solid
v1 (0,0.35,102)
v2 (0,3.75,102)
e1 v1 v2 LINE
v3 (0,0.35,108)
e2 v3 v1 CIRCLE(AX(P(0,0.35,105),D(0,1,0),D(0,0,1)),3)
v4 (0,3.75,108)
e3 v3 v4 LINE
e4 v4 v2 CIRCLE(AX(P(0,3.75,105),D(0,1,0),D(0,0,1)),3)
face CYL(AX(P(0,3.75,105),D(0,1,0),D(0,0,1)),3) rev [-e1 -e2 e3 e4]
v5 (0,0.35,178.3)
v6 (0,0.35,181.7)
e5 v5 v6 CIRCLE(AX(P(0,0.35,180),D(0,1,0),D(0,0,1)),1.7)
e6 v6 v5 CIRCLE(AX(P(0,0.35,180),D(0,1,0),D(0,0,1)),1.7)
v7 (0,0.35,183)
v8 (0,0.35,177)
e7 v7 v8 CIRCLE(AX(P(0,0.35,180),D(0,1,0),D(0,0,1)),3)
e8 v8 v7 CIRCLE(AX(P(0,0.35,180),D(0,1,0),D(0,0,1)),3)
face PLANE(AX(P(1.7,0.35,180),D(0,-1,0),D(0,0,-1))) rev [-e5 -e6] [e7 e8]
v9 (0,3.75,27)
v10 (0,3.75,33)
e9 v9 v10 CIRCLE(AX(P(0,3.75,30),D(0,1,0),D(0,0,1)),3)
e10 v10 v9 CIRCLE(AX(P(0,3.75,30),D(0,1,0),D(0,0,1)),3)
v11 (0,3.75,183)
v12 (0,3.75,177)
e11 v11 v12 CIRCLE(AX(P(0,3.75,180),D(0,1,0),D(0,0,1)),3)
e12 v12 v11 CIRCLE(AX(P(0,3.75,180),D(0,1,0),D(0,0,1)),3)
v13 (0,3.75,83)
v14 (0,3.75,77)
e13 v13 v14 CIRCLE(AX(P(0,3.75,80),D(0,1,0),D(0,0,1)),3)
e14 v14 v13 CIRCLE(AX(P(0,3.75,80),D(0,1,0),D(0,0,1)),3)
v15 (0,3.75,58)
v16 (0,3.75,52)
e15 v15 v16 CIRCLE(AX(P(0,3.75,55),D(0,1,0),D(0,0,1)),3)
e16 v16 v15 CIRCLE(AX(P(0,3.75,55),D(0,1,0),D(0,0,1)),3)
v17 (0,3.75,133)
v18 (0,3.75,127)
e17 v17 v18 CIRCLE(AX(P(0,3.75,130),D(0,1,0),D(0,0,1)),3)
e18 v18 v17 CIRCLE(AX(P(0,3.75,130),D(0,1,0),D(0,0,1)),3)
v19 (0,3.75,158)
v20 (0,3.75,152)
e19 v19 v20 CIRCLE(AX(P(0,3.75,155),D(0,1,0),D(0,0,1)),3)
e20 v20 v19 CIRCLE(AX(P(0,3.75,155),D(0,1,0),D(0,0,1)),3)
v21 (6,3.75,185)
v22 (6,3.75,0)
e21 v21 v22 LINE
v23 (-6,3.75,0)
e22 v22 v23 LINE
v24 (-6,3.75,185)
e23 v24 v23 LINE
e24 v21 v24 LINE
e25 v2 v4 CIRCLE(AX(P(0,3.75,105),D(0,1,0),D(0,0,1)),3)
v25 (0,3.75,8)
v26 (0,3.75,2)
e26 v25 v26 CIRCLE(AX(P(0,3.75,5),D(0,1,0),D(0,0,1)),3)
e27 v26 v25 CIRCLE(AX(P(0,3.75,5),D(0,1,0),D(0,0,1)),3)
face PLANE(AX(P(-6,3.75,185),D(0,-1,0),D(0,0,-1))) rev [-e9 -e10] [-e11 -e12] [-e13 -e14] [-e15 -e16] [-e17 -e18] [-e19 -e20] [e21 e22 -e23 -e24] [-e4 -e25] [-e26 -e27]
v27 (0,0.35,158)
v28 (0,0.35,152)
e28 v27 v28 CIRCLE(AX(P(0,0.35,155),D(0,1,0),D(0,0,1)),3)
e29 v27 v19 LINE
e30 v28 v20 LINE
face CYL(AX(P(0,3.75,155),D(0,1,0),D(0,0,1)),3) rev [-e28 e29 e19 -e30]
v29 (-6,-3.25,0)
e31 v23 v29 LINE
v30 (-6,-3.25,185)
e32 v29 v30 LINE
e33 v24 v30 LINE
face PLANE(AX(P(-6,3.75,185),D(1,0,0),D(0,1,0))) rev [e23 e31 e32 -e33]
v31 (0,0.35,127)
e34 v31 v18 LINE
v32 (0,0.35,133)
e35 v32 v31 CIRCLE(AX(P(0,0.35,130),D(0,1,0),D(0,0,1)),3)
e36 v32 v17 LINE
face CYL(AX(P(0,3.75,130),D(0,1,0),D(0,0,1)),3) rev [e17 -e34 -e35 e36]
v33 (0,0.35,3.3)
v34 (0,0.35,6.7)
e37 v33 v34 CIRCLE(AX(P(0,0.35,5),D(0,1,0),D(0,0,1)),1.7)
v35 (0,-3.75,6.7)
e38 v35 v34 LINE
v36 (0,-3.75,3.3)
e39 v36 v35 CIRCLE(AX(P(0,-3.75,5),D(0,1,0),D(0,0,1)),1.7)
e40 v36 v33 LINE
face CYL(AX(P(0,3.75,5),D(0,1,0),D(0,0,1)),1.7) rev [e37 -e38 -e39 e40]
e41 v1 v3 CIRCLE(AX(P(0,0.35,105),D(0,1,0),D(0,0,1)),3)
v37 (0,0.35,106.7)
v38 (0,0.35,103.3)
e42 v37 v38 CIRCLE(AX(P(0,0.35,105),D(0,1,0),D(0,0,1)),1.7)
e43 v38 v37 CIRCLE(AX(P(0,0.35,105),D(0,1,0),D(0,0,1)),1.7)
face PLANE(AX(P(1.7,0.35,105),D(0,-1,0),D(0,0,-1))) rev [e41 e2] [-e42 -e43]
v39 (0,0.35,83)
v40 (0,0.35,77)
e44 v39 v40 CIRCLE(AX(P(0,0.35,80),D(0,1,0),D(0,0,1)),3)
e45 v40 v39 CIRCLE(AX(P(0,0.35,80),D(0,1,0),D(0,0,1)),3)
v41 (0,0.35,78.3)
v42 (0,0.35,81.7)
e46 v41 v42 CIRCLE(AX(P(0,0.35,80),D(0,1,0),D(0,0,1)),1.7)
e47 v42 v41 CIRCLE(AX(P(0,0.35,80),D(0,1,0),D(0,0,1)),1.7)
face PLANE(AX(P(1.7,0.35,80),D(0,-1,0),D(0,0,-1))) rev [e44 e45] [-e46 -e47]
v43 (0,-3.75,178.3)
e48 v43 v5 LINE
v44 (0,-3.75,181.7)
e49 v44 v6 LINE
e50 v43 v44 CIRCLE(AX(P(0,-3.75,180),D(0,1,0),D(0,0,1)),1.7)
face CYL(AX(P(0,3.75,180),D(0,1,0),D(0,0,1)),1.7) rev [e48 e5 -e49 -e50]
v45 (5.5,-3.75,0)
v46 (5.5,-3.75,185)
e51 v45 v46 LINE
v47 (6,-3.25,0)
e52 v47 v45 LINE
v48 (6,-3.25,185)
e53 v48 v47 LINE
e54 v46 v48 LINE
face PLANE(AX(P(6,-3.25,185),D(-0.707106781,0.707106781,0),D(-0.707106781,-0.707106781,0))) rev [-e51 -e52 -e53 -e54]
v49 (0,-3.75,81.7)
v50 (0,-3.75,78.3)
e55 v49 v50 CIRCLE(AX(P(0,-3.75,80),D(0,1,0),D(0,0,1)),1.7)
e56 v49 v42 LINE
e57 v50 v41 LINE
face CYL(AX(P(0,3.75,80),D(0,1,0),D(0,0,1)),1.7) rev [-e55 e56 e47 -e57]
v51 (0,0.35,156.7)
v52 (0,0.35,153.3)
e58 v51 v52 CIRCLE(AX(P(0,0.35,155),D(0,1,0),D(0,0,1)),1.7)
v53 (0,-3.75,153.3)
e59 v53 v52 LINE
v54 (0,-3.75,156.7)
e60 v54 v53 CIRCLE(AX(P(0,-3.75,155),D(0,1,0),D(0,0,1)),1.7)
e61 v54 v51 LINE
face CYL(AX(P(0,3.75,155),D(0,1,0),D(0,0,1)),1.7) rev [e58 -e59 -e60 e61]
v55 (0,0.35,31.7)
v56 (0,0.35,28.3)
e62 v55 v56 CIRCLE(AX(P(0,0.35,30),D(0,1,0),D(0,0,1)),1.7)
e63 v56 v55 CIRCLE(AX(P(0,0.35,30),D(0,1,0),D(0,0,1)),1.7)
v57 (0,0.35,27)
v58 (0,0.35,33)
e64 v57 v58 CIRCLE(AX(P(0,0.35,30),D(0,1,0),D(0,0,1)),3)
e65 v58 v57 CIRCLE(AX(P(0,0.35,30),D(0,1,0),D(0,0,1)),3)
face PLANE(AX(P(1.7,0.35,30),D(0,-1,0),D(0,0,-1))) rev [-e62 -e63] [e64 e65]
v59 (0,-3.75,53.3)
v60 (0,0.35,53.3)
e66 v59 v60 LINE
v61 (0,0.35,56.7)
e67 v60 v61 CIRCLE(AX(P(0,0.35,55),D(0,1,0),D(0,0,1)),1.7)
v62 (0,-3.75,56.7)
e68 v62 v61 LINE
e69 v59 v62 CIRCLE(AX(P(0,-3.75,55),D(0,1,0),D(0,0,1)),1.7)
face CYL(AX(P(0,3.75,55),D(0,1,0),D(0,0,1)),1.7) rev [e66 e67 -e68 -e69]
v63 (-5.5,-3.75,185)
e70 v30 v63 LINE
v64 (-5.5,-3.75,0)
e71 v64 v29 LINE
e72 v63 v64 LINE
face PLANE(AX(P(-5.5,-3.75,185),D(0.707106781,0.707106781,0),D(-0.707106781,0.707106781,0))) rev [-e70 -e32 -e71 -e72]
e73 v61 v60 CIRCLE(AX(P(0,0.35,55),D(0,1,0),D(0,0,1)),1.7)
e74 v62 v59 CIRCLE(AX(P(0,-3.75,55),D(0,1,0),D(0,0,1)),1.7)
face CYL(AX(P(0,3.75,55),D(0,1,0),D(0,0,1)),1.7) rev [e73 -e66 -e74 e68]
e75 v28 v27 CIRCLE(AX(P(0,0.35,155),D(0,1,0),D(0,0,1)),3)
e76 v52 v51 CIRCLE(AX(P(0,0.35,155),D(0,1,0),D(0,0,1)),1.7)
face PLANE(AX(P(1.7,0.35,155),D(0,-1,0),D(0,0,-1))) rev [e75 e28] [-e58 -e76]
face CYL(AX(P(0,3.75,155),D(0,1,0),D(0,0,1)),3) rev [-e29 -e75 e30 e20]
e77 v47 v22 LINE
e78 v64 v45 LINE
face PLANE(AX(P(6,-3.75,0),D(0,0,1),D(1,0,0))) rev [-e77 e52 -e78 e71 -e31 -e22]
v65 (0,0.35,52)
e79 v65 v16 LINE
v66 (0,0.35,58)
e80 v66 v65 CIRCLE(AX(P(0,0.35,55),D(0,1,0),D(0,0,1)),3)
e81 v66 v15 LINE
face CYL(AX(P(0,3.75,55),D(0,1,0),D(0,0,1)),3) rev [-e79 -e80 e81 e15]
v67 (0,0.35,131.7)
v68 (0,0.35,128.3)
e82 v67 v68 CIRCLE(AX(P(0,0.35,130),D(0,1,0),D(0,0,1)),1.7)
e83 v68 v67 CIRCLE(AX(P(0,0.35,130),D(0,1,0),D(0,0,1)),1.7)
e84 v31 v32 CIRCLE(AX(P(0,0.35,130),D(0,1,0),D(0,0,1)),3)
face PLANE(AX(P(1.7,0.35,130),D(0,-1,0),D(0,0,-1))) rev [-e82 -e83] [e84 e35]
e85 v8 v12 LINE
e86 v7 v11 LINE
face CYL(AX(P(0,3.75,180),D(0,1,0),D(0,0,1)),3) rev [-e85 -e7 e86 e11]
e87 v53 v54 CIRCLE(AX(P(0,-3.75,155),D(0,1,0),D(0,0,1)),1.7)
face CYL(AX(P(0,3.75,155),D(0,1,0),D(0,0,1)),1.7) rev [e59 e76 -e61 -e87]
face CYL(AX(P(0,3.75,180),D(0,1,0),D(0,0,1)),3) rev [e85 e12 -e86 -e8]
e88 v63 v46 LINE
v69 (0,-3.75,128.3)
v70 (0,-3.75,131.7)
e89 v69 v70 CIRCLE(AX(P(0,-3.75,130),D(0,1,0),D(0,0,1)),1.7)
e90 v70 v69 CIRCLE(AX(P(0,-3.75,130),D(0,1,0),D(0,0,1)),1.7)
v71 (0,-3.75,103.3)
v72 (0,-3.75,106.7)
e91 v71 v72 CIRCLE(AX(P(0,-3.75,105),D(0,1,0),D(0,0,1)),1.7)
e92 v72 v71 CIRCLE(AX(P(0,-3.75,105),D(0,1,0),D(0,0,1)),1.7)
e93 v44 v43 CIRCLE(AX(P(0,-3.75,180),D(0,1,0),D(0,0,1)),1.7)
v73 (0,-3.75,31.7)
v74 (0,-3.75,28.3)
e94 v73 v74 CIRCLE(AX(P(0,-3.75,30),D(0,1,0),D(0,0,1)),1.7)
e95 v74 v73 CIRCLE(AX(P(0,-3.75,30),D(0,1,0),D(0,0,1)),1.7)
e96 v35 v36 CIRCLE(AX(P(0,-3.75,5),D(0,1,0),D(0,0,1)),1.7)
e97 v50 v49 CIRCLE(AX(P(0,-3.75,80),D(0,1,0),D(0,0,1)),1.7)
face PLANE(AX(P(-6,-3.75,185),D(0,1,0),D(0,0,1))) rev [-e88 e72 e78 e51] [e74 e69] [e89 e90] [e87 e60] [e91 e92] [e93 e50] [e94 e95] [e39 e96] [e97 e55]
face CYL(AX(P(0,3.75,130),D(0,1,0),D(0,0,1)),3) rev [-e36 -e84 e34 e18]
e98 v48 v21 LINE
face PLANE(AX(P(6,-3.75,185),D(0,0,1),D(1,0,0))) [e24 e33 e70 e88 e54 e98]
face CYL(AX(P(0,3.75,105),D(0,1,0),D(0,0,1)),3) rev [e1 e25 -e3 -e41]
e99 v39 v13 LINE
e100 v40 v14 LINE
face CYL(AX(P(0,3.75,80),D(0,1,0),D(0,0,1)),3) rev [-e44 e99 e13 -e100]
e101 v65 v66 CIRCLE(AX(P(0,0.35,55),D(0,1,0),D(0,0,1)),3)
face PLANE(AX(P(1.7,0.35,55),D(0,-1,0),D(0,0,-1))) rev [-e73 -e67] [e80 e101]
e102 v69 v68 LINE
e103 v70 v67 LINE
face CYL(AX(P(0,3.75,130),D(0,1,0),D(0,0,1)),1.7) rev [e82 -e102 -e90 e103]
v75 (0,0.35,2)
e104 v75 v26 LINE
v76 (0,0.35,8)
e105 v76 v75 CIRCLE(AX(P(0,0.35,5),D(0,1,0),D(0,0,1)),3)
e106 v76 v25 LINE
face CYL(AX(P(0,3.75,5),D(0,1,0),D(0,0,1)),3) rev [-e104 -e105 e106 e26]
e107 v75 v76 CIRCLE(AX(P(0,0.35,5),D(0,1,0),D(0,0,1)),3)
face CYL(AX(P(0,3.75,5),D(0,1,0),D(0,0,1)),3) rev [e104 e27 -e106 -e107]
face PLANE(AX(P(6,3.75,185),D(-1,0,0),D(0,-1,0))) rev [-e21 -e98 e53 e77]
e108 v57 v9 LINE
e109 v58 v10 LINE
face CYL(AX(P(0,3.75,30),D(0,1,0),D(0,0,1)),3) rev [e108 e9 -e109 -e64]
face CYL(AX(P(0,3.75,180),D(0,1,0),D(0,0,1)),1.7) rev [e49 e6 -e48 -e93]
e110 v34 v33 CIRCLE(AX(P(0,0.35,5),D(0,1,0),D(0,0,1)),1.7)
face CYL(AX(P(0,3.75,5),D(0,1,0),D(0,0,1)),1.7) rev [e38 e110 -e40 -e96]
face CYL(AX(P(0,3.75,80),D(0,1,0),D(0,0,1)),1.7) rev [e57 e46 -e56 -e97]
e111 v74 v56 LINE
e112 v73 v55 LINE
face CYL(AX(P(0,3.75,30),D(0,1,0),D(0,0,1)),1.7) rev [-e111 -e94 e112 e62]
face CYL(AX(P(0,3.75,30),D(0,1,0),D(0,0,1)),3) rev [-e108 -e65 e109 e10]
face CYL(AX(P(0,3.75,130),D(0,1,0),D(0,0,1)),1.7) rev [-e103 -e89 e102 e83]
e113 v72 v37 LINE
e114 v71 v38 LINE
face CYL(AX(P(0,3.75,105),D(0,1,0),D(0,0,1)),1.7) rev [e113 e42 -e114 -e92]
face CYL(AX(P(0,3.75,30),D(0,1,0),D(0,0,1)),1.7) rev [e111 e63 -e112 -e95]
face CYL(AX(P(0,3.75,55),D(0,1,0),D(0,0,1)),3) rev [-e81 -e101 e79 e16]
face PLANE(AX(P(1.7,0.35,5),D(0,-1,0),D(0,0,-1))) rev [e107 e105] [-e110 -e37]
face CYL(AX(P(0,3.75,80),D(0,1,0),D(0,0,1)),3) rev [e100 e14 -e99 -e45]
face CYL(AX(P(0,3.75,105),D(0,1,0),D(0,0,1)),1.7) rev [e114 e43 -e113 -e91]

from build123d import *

# Parameters (mm, degrees)
SKETCH1_W                                            = 12
SKETCH1_H                                            = 7.5
BOSS_EXTRUDE1_DEPTH                                  = 185
CHAMFER1_SIZE                                        = 0.5
HOLE_SIZE_PER_SOCKET_HEAD_CAP_SCREW_TYPE_D           = 3.4
HOLE_SIZE_PER_SOCKET_HEAD_CAP_SCREW_TYPE_CBORE_D     = 6
HOLE_SIZE_PER_SOCKET_HEAD_CAP_SCREW_TYPE_CBORE_DEPTH = 3.4
LPATTERN1_COUNT                                      = 8
LPATTERN1_PITCH                                      = 25


with BuildPart() as part:
    # Sketch1 → Boss-Extrude1 (new body)
    with BuildSketch(Plane.XY):
        Rectangle(SKETCH1_W, SKETCH1_H)
    extrude(amount=BOSS_EXTRUDE1_DEPTH)

    # Chamfer1
    chamfer1_edges = [part.edges().sort_by_distance(p)[0] for p in [
        (6, -3.75, 92.5),
        (-6, -3.75, 92.5),
    ]]
    chamfer(chamfer1_edges, length=CHAMFER1_SIZE)

    # Hole size per socket head cap screw type1 (through all)
    with Locations(Plane(origin=(0, 3.75, 0), x_dir=(-1, 0, 0), z_dir=(0, 1, 0))):
        with Locations((0, 5)):
            hole_size_per_socket_head_cap_screw_type = CounterBoreHole(HOLE_SIZE_PER_SOCKET_HEAD_CAP_SCREW_TYPE_D / 2, HOLE_SIZE_PER_SOCKET_HEAD_CAP_SCREW_TYPE_CBORE_D / 2, HOLE_SIZE_PER_SOCKET_HEAD_CAP_SCREW_TYPE_CBORE_DEPTH)

    # LPattern1: Hole size per socket head cap screw type1 ×8
    with Locations(*[(0, 0, i * LPATTERN1_PITCH) for i in range(1, LPATTERN1_COUNT)]):
        add(hole_size_per_socket_head_cap_screw_type, mode=Mode.SUBTRACT)


solid = part.part
